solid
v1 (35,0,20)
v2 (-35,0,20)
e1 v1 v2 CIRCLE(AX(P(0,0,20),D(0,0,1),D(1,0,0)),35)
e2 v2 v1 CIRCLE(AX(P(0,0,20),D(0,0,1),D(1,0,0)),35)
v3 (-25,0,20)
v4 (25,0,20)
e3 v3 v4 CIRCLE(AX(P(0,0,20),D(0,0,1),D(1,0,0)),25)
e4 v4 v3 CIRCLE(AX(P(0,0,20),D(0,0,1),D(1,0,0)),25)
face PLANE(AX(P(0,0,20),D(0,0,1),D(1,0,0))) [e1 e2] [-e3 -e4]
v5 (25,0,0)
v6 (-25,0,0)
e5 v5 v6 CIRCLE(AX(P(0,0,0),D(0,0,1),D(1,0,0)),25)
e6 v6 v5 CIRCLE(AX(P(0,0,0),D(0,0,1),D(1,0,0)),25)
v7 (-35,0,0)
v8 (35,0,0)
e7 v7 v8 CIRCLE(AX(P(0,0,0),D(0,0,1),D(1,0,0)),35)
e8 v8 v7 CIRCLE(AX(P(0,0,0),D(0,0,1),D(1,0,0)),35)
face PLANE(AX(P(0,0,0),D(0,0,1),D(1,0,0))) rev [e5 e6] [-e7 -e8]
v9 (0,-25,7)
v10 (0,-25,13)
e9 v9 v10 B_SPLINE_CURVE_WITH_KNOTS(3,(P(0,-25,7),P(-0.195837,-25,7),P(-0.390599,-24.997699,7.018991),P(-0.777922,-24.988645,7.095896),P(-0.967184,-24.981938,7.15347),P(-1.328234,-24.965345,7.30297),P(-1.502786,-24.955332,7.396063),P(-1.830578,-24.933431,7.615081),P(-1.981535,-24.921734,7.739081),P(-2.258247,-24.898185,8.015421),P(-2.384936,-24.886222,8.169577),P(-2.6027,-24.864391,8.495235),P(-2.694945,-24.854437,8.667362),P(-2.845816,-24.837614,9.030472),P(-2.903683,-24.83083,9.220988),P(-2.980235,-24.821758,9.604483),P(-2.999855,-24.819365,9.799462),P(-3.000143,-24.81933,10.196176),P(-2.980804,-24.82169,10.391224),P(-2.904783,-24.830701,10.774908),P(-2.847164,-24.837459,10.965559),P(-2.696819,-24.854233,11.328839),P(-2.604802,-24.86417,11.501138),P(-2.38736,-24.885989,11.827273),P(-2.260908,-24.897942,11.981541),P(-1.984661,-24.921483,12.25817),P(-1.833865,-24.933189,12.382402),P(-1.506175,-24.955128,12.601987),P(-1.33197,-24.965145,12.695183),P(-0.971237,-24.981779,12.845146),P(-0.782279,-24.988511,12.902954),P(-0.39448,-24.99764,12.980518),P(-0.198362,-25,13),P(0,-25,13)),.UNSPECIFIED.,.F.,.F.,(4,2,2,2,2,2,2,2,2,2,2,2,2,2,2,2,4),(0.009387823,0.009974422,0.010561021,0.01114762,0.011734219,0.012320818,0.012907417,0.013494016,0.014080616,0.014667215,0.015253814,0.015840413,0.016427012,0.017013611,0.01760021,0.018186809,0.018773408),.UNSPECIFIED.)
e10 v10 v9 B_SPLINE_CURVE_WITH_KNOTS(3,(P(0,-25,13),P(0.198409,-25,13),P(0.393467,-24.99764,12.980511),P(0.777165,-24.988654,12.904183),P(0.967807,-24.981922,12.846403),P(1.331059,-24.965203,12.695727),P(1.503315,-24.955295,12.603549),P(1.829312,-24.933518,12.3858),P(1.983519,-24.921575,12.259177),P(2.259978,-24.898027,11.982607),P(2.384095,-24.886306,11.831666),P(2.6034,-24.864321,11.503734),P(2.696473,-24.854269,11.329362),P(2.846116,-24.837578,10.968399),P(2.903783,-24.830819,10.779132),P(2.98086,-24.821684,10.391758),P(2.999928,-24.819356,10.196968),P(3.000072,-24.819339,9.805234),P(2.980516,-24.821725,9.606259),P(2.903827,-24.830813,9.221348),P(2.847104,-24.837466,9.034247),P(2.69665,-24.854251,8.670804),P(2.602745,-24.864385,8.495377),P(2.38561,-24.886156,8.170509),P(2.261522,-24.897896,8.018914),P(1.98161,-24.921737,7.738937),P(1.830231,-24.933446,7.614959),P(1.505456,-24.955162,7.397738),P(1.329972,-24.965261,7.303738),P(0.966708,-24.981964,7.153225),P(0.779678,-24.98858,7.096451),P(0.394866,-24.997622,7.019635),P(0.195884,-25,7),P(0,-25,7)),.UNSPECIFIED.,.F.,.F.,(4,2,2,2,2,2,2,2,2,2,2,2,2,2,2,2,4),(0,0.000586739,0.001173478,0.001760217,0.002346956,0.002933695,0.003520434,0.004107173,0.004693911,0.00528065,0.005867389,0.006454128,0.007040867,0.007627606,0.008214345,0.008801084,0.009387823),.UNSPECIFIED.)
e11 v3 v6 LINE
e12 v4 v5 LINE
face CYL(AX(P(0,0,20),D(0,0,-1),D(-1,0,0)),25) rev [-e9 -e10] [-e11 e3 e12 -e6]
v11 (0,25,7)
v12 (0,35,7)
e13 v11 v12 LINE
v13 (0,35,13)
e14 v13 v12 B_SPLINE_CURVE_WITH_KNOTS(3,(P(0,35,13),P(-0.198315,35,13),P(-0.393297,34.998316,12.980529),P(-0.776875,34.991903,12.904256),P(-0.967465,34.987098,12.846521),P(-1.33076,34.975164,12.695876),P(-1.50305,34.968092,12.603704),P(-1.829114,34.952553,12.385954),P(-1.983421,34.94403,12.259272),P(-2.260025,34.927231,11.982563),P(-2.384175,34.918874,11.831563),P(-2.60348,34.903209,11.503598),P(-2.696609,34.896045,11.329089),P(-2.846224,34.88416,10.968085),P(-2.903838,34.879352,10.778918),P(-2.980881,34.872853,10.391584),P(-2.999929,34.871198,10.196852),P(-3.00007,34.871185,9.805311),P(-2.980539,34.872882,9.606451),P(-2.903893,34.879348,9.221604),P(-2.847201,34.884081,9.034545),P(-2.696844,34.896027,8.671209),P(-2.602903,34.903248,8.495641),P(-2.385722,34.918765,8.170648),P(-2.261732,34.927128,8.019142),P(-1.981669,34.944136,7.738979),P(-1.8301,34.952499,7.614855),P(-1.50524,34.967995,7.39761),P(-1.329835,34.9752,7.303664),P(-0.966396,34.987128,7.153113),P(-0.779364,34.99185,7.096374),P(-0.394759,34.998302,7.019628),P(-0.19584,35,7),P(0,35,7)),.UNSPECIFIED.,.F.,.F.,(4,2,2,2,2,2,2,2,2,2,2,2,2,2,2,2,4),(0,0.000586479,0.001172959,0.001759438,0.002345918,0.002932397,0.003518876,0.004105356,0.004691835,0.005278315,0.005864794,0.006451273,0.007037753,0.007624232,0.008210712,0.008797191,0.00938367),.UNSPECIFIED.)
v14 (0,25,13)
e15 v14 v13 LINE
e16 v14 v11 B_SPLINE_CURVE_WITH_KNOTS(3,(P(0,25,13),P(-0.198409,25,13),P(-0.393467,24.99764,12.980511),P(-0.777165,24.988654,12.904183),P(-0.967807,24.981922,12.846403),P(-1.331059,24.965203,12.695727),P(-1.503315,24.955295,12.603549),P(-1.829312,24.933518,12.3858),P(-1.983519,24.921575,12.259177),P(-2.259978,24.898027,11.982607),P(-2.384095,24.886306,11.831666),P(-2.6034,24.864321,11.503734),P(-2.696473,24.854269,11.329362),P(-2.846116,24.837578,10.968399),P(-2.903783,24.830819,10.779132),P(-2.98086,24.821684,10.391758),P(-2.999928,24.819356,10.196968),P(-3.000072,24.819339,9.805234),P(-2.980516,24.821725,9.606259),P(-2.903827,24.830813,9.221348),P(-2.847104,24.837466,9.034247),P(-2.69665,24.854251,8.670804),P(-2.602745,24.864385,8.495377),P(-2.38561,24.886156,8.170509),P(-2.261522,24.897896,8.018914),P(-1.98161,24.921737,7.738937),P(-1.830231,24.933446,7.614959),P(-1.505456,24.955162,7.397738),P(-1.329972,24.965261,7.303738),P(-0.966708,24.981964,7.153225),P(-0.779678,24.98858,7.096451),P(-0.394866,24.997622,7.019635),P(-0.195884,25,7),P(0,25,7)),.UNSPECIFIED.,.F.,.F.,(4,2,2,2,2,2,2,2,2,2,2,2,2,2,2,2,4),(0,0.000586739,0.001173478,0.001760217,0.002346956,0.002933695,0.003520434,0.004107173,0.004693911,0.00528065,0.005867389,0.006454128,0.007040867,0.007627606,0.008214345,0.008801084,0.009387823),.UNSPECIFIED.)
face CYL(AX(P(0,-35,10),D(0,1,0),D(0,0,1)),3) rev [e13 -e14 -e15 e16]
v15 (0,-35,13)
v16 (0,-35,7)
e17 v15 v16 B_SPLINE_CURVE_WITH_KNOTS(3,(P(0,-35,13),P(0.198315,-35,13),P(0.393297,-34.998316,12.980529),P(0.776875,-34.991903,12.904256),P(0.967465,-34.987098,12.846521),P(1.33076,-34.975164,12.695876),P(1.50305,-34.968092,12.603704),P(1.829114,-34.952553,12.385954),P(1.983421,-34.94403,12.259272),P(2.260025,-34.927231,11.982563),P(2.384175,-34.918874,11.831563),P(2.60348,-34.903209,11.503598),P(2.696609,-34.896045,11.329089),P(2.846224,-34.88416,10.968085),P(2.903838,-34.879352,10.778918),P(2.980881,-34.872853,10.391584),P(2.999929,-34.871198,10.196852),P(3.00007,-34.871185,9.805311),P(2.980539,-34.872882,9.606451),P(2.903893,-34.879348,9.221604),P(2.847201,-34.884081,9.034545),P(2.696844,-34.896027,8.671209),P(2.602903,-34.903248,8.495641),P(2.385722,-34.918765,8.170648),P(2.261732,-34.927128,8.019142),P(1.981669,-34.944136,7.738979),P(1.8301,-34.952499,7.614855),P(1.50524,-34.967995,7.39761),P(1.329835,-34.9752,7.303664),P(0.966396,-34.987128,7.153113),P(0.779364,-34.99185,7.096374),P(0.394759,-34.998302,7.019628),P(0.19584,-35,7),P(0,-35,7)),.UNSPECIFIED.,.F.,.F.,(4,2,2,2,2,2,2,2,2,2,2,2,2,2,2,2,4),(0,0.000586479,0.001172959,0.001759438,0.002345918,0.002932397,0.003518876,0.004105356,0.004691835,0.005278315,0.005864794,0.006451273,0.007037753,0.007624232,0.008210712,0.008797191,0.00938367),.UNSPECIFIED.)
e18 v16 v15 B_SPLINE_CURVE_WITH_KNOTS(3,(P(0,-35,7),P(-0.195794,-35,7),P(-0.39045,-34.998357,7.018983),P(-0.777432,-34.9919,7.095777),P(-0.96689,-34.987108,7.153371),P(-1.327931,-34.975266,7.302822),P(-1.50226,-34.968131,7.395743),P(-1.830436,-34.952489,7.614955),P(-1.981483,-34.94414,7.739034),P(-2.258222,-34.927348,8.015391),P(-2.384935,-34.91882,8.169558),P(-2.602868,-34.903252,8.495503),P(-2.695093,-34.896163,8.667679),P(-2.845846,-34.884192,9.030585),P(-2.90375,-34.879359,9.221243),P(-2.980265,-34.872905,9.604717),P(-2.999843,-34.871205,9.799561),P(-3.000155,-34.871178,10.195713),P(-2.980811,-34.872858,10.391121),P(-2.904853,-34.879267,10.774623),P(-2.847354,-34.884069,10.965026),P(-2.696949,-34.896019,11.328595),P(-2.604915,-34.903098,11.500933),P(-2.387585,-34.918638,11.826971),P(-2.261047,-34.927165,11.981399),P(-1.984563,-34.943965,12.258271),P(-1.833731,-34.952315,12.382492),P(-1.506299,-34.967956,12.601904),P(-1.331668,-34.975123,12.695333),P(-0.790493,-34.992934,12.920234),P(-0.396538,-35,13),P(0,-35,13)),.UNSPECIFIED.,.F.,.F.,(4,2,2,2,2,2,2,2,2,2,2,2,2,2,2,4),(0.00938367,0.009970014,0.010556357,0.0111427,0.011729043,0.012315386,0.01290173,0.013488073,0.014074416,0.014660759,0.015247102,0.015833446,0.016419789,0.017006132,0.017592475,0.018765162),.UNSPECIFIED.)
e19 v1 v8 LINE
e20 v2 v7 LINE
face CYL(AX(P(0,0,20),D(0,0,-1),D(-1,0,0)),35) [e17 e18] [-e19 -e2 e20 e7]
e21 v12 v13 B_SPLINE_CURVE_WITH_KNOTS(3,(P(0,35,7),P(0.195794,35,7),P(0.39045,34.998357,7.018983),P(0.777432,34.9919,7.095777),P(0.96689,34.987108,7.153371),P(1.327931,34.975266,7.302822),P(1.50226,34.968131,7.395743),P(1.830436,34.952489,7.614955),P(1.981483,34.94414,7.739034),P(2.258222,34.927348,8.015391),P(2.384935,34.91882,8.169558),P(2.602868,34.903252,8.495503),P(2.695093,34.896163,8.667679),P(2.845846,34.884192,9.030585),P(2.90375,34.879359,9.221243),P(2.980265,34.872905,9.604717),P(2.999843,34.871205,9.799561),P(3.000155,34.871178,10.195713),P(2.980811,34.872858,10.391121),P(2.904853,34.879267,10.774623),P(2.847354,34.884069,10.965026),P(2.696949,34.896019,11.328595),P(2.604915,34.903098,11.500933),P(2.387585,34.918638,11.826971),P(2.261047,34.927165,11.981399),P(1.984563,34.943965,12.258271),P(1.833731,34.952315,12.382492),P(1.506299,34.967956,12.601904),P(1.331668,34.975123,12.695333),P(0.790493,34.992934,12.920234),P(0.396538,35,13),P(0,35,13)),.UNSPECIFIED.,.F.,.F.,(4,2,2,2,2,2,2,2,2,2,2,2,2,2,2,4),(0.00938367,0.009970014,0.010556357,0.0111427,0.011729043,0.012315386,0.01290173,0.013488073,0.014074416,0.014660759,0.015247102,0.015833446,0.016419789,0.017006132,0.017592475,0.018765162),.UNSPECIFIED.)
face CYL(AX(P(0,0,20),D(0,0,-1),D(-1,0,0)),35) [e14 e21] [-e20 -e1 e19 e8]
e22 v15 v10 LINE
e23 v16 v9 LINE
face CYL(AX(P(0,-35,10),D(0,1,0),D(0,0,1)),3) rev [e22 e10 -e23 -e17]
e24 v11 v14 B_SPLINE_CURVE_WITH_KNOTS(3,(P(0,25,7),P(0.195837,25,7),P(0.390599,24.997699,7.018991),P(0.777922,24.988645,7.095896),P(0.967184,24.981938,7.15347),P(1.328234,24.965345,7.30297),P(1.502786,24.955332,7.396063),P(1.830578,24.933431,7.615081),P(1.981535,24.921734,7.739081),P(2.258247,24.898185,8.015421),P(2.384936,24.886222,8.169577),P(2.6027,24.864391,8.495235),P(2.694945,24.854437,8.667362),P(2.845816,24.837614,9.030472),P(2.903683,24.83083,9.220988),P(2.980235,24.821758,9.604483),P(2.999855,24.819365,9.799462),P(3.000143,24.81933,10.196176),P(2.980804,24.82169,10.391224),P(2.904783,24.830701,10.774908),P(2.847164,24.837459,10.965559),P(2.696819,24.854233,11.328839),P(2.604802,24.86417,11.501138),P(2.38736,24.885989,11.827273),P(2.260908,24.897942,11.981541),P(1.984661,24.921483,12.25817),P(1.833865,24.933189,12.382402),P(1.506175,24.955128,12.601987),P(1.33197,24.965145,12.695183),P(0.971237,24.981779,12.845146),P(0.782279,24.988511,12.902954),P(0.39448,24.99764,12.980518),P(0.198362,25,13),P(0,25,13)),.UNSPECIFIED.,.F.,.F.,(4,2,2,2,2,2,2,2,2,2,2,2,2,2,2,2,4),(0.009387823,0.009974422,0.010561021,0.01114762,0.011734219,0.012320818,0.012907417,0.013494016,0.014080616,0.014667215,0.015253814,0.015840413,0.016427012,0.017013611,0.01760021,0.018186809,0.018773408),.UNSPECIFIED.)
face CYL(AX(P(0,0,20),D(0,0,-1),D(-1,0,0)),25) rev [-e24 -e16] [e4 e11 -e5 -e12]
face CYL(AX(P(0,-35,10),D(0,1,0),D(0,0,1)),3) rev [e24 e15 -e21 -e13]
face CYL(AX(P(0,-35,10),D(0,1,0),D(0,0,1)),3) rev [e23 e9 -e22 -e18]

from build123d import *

# Parameters (mm, degrees)
COLLAR_RING_SKETCH_70_50_R   = 35
COLLAR_RING_SKETCH_70_50_R_2 = 25
COLLAR_RING_20_THICK_DEPTH   = 20
RADIAL_PIN_HOLE_6_DEPTH      = 54.38539126
RADIAL_PIN_HOLE_6_DEPTH_BACK = 54.38539126
PIN_HOLE_SKETCH_6_R          = 3


with BuildPart() as part:
    # Collar Ring Sketch Ø70-Ø50 → Collar Ring 20 Thick (new body)
    with BuildSketch(Plane.XY):
        Circle(COLLAR_RING_SKETCH_70_50_R)
        Circle(COLLAR_RING_SKETCH_70_50_R_2, mode=Mode.SUBTRACT)
    extrude(amount=COLLAR_RING_20_THICK_DEPTH)

    # Pin Hole Sketch Ø6 → Radial Pin Hole Ø6 (cut, two sides: drawn at the far end of the back side and taken through both)
    with BuildSketch(Plane(origin=(0, 0, 0), x_dir=(1, 0, 0), z_dir=(0, 1, 0)).offset(-RADIAL_PIN_HOLE_6_DEPTH_BACK)):
        with Locations(Location((0, -10, 0), (0, 0, 270))):
            Circle(PIN_HOLE_SKETCH_6_R)
    extrude(amount=RADIAL_PIN_HOLE_6_DEPTH + RADIAL_PIN_HOLE_6_DEPTH_BACK, mode=Mode.SUBTRACT)


solid = part.part
